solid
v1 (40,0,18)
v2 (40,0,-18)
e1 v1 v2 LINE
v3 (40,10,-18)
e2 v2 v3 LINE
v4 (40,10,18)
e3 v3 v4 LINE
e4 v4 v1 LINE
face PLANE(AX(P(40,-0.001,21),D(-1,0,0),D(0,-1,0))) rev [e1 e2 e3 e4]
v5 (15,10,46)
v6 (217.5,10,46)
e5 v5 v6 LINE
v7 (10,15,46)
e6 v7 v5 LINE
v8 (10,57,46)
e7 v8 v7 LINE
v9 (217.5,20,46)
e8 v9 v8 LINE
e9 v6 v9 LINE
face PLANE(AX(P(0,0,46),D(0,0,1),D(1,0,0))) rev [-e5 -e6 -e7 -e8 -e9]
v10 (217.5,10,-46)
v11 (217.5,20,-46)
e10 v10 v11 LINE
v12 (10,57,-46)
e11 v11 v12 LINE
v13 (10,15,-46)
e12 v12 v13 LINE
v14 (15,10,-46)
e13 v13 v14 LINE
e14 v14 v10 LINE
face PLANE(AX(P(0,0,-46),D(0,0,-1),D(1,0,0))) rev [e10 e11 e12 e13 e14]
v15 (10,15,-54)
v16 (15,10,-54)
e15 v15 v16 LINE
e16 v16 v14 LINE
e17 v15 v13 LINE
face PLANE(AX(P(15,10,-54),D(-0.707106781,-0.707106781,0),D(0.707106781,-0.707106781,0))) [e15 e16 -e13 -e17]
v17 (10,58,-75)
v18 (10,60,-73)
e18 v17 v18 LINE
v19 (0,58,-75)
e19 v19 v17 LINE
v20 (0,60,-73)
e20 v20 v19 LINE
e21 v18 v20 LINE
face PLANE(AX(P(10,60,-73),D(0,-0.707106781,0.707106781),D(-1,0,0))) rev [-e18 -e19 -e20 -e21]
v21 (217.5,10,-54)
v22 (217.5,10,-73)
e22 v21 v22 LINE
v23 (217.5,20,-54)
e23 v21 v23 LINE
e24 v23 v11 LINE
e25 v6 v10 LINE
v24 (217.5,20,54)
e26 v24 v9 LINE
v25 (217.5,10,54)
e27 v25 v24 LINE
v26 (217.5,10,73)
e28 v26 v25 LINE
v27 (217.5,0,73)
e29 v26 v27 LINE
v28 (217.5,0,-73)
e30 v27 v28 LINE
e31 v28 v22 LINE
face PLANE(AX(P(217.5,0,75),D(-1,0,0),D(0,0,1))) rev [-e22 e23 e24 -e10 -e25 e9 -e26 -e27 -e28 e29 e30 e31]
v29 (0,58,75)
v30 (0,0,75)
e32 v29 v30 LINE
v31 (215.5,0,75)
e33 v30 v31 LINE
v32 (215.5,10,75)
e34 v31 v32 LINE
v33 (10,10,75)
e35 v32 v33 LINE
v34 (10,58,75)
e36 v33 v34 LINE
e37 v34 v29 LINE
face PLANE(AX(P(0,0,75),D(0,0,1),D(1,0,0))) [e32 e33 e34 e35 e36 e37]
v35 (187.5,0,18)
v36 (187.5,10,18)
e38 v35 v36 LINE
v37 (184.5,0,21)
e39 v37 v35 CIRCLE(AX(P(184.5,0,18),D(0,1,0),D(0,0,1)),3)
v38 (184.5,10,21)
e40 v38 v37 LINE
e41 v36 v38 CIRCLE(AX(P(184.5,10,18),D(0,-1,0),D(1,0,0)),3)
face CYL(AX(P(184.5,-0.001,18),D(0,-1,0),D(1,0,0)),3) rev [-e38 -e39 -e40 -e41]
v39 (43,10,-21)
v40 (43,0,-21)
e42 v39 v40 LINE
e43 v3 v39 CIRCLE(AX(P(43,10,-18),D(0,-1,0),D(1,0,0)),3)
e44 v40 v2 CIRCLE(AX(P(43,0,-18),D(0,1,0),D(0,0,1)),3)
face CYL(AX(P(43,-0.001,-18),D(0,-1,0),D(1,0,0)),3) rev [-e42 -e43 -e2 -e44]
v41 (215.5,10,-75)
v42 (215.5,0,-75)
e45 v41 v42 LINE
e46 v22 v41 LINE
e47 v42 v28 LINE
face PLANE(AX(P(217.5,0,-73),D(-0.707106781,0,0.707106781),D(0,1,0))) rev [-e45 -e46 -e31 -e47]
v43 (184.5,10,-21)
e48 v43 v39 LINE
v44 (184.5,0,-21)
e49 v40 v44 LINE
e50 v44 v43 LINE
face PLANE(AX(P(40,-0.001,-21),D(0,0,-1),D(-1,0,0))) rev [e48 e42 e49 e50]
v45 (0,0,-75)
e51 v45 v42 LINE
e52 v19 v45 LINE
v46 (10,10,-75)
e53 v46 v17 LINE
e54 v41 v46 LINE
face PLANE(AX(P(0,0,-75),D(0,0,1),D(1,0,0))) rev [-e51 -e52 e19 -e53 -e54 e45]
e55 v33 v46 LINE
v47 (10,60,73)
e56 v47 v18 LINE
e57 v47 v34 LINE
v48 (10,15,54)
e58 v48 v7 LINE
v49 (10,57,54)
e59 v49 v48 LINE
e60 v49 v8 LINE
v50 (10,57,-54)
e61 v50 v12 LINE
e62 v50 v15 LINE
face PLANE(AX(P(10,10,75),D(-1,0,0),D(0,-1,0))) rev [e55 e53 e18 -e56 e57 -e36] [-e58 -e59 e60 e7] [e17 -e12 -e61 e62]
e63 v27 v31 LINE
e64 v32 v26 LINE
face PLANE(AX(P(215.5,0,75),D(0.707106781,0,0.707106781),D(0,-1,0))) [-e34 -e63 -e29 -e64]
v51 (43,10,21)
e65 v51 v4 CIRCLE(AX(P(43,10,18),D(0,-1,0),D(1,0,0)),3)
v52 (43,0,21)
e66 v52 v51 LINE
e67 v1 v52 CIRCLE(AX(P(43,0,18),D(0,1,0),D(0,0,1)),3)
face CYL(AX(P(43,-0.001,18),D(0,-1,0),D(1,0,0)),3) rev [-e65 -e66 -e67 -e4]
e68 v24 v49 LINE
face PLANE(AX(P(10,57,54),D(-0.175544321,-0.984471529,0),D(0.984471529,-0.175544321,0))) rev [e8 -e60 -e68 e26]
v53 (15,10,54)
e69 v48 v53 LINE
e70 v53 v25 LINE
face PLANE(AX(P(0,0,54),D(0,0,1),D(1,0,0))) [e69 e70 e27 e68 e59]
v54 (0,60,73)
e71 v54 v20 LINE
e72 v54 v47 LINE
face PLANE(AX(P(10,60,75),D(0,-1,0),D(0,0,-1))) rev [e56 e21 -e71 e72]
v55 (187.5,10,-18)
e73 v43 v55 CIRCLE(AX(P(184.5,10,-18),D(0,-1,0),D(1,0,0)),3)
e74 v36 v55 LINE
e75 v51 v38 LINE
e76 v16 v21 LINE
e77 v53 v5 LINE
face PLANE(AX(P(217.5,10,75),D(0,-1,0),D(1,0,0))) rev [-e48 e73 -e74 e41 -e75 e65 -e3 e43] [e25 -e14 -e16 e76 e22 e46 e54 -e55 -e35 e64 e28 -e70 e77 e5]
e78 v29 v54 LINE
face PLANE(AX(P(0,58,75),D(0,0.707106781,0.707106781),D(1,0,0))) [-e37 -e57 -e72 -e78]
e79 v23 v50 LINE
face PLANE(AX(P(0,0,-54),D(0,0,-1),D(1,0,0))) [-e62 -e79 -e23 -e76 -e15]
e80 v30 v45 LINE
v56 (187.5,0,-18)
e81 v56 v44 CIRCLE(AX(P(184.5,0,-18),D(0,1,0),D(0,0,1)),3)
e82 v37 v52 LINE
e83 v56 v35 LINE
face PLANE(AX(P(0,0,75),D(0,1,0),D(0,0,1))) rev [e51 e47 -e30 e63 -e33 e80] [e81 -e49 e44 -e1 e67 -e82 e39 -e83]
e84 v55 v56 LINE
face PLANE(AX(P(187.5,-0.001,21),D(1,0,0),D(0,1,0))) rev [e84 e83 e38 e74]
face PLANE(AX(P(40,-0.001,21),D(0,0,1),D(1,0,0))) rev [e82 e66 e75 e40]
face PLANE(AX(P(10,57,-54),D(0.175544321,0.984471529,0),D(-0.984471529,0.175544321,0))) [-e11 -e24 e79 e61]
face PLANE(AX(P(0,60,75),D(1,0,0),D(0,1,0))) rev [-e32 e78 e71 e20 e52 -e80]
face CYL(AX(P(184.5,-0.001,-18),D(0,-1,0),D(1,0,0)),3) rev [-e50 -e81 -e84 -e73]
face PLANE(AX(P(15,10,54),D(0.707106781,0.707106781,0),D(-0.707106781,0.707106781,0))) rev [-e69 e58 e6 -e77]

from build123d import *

# Parameters (mm, degrees)
EXTRUDE_1_DEPTH     = 75
EXTRUDE_START       = 50
EXTRUDE_2_DEPTH     = 4
CHAMFER_1_SIZE      = 2
CUT_EXTRUDE_1_REACH = 237.438
SKETCH_3_W          = 147.5
SKETCH_3_H          = 42
FILLET_1_R          = 3


with BuildPart() as part:
    # 草图1 → 凸台-拉伸1 (new, symmetric)
    with BuildSketch(Plane.XY):
        Polygon((0, 0), (217.5, 0), (217.5, 10), (10, 10), (10, 60), (0, 60), align=None)
    extrude(amount=EXTRUDE_1_DEPTH, both=True)

    # 草图2 → 凸台-拉伸2 (add, symmetric)
    with BuildSketch(Plane.XY.offset(EXTRUDE_START)):
        Polygon((10, 57), (217.5, 20), (217.5, 10), (15, 10), (10, 15), align=None)
    extrude_2 = extrude(amount=EXTRUDE_2_DEPTH, both=True)

    # 倒角1
    chamfer_1_edges = [part.edges().sort_by_distance(p)[0] for p in [
        (217.5, 5, 75),
        (5, 60, 75),
        (5, 60, -75),
        (217.5, 5, -75),
    ]]
    chamfer(chamfer_1_edges, length=CHAMFER_1_SIZE)

    # 镜向1: 凸台-拉伸2 across plane
    add(extrude_2.mirror(Plane.XY))

    # 草图3 → 切除-拉伸1 (cut, up to next)
    with BuildSketch(Plane(origin=(0, 10, 0), x_dir=(1, 0, 0), z_dir=(0, 1, 0)), mode=Mode.PRIVATE) as cut_extrude_1_sk1:
        with Locations((113.75, 0)):
            Rectangle(SKETCH_3_W, SKETCH_3_H)
    cut_extrude_1_tool1 = extrude(cut_extrude_1_sk1.sketch, amount=-CUT_EXTRUDE_1_REACH, mode=Mode.PRIVATE) & part.part
    add(cut_extrude_1_tool1.solids().sort_by_distance((113.75, 10, 0))[0], mode=Mode.SUBTRACT)

    # 圆角1
    fillet_1_edges = [part.edges().sort_by_distance(p)[0] for p in [
        (187.5, 5, -21),
        (187.5, 5, 21),
        (40, 5, 21),
        (40, 5, -21),
    ]]
    fillet(fillet_1_edges, radius=FILLET_1_R)


solid = part.part
